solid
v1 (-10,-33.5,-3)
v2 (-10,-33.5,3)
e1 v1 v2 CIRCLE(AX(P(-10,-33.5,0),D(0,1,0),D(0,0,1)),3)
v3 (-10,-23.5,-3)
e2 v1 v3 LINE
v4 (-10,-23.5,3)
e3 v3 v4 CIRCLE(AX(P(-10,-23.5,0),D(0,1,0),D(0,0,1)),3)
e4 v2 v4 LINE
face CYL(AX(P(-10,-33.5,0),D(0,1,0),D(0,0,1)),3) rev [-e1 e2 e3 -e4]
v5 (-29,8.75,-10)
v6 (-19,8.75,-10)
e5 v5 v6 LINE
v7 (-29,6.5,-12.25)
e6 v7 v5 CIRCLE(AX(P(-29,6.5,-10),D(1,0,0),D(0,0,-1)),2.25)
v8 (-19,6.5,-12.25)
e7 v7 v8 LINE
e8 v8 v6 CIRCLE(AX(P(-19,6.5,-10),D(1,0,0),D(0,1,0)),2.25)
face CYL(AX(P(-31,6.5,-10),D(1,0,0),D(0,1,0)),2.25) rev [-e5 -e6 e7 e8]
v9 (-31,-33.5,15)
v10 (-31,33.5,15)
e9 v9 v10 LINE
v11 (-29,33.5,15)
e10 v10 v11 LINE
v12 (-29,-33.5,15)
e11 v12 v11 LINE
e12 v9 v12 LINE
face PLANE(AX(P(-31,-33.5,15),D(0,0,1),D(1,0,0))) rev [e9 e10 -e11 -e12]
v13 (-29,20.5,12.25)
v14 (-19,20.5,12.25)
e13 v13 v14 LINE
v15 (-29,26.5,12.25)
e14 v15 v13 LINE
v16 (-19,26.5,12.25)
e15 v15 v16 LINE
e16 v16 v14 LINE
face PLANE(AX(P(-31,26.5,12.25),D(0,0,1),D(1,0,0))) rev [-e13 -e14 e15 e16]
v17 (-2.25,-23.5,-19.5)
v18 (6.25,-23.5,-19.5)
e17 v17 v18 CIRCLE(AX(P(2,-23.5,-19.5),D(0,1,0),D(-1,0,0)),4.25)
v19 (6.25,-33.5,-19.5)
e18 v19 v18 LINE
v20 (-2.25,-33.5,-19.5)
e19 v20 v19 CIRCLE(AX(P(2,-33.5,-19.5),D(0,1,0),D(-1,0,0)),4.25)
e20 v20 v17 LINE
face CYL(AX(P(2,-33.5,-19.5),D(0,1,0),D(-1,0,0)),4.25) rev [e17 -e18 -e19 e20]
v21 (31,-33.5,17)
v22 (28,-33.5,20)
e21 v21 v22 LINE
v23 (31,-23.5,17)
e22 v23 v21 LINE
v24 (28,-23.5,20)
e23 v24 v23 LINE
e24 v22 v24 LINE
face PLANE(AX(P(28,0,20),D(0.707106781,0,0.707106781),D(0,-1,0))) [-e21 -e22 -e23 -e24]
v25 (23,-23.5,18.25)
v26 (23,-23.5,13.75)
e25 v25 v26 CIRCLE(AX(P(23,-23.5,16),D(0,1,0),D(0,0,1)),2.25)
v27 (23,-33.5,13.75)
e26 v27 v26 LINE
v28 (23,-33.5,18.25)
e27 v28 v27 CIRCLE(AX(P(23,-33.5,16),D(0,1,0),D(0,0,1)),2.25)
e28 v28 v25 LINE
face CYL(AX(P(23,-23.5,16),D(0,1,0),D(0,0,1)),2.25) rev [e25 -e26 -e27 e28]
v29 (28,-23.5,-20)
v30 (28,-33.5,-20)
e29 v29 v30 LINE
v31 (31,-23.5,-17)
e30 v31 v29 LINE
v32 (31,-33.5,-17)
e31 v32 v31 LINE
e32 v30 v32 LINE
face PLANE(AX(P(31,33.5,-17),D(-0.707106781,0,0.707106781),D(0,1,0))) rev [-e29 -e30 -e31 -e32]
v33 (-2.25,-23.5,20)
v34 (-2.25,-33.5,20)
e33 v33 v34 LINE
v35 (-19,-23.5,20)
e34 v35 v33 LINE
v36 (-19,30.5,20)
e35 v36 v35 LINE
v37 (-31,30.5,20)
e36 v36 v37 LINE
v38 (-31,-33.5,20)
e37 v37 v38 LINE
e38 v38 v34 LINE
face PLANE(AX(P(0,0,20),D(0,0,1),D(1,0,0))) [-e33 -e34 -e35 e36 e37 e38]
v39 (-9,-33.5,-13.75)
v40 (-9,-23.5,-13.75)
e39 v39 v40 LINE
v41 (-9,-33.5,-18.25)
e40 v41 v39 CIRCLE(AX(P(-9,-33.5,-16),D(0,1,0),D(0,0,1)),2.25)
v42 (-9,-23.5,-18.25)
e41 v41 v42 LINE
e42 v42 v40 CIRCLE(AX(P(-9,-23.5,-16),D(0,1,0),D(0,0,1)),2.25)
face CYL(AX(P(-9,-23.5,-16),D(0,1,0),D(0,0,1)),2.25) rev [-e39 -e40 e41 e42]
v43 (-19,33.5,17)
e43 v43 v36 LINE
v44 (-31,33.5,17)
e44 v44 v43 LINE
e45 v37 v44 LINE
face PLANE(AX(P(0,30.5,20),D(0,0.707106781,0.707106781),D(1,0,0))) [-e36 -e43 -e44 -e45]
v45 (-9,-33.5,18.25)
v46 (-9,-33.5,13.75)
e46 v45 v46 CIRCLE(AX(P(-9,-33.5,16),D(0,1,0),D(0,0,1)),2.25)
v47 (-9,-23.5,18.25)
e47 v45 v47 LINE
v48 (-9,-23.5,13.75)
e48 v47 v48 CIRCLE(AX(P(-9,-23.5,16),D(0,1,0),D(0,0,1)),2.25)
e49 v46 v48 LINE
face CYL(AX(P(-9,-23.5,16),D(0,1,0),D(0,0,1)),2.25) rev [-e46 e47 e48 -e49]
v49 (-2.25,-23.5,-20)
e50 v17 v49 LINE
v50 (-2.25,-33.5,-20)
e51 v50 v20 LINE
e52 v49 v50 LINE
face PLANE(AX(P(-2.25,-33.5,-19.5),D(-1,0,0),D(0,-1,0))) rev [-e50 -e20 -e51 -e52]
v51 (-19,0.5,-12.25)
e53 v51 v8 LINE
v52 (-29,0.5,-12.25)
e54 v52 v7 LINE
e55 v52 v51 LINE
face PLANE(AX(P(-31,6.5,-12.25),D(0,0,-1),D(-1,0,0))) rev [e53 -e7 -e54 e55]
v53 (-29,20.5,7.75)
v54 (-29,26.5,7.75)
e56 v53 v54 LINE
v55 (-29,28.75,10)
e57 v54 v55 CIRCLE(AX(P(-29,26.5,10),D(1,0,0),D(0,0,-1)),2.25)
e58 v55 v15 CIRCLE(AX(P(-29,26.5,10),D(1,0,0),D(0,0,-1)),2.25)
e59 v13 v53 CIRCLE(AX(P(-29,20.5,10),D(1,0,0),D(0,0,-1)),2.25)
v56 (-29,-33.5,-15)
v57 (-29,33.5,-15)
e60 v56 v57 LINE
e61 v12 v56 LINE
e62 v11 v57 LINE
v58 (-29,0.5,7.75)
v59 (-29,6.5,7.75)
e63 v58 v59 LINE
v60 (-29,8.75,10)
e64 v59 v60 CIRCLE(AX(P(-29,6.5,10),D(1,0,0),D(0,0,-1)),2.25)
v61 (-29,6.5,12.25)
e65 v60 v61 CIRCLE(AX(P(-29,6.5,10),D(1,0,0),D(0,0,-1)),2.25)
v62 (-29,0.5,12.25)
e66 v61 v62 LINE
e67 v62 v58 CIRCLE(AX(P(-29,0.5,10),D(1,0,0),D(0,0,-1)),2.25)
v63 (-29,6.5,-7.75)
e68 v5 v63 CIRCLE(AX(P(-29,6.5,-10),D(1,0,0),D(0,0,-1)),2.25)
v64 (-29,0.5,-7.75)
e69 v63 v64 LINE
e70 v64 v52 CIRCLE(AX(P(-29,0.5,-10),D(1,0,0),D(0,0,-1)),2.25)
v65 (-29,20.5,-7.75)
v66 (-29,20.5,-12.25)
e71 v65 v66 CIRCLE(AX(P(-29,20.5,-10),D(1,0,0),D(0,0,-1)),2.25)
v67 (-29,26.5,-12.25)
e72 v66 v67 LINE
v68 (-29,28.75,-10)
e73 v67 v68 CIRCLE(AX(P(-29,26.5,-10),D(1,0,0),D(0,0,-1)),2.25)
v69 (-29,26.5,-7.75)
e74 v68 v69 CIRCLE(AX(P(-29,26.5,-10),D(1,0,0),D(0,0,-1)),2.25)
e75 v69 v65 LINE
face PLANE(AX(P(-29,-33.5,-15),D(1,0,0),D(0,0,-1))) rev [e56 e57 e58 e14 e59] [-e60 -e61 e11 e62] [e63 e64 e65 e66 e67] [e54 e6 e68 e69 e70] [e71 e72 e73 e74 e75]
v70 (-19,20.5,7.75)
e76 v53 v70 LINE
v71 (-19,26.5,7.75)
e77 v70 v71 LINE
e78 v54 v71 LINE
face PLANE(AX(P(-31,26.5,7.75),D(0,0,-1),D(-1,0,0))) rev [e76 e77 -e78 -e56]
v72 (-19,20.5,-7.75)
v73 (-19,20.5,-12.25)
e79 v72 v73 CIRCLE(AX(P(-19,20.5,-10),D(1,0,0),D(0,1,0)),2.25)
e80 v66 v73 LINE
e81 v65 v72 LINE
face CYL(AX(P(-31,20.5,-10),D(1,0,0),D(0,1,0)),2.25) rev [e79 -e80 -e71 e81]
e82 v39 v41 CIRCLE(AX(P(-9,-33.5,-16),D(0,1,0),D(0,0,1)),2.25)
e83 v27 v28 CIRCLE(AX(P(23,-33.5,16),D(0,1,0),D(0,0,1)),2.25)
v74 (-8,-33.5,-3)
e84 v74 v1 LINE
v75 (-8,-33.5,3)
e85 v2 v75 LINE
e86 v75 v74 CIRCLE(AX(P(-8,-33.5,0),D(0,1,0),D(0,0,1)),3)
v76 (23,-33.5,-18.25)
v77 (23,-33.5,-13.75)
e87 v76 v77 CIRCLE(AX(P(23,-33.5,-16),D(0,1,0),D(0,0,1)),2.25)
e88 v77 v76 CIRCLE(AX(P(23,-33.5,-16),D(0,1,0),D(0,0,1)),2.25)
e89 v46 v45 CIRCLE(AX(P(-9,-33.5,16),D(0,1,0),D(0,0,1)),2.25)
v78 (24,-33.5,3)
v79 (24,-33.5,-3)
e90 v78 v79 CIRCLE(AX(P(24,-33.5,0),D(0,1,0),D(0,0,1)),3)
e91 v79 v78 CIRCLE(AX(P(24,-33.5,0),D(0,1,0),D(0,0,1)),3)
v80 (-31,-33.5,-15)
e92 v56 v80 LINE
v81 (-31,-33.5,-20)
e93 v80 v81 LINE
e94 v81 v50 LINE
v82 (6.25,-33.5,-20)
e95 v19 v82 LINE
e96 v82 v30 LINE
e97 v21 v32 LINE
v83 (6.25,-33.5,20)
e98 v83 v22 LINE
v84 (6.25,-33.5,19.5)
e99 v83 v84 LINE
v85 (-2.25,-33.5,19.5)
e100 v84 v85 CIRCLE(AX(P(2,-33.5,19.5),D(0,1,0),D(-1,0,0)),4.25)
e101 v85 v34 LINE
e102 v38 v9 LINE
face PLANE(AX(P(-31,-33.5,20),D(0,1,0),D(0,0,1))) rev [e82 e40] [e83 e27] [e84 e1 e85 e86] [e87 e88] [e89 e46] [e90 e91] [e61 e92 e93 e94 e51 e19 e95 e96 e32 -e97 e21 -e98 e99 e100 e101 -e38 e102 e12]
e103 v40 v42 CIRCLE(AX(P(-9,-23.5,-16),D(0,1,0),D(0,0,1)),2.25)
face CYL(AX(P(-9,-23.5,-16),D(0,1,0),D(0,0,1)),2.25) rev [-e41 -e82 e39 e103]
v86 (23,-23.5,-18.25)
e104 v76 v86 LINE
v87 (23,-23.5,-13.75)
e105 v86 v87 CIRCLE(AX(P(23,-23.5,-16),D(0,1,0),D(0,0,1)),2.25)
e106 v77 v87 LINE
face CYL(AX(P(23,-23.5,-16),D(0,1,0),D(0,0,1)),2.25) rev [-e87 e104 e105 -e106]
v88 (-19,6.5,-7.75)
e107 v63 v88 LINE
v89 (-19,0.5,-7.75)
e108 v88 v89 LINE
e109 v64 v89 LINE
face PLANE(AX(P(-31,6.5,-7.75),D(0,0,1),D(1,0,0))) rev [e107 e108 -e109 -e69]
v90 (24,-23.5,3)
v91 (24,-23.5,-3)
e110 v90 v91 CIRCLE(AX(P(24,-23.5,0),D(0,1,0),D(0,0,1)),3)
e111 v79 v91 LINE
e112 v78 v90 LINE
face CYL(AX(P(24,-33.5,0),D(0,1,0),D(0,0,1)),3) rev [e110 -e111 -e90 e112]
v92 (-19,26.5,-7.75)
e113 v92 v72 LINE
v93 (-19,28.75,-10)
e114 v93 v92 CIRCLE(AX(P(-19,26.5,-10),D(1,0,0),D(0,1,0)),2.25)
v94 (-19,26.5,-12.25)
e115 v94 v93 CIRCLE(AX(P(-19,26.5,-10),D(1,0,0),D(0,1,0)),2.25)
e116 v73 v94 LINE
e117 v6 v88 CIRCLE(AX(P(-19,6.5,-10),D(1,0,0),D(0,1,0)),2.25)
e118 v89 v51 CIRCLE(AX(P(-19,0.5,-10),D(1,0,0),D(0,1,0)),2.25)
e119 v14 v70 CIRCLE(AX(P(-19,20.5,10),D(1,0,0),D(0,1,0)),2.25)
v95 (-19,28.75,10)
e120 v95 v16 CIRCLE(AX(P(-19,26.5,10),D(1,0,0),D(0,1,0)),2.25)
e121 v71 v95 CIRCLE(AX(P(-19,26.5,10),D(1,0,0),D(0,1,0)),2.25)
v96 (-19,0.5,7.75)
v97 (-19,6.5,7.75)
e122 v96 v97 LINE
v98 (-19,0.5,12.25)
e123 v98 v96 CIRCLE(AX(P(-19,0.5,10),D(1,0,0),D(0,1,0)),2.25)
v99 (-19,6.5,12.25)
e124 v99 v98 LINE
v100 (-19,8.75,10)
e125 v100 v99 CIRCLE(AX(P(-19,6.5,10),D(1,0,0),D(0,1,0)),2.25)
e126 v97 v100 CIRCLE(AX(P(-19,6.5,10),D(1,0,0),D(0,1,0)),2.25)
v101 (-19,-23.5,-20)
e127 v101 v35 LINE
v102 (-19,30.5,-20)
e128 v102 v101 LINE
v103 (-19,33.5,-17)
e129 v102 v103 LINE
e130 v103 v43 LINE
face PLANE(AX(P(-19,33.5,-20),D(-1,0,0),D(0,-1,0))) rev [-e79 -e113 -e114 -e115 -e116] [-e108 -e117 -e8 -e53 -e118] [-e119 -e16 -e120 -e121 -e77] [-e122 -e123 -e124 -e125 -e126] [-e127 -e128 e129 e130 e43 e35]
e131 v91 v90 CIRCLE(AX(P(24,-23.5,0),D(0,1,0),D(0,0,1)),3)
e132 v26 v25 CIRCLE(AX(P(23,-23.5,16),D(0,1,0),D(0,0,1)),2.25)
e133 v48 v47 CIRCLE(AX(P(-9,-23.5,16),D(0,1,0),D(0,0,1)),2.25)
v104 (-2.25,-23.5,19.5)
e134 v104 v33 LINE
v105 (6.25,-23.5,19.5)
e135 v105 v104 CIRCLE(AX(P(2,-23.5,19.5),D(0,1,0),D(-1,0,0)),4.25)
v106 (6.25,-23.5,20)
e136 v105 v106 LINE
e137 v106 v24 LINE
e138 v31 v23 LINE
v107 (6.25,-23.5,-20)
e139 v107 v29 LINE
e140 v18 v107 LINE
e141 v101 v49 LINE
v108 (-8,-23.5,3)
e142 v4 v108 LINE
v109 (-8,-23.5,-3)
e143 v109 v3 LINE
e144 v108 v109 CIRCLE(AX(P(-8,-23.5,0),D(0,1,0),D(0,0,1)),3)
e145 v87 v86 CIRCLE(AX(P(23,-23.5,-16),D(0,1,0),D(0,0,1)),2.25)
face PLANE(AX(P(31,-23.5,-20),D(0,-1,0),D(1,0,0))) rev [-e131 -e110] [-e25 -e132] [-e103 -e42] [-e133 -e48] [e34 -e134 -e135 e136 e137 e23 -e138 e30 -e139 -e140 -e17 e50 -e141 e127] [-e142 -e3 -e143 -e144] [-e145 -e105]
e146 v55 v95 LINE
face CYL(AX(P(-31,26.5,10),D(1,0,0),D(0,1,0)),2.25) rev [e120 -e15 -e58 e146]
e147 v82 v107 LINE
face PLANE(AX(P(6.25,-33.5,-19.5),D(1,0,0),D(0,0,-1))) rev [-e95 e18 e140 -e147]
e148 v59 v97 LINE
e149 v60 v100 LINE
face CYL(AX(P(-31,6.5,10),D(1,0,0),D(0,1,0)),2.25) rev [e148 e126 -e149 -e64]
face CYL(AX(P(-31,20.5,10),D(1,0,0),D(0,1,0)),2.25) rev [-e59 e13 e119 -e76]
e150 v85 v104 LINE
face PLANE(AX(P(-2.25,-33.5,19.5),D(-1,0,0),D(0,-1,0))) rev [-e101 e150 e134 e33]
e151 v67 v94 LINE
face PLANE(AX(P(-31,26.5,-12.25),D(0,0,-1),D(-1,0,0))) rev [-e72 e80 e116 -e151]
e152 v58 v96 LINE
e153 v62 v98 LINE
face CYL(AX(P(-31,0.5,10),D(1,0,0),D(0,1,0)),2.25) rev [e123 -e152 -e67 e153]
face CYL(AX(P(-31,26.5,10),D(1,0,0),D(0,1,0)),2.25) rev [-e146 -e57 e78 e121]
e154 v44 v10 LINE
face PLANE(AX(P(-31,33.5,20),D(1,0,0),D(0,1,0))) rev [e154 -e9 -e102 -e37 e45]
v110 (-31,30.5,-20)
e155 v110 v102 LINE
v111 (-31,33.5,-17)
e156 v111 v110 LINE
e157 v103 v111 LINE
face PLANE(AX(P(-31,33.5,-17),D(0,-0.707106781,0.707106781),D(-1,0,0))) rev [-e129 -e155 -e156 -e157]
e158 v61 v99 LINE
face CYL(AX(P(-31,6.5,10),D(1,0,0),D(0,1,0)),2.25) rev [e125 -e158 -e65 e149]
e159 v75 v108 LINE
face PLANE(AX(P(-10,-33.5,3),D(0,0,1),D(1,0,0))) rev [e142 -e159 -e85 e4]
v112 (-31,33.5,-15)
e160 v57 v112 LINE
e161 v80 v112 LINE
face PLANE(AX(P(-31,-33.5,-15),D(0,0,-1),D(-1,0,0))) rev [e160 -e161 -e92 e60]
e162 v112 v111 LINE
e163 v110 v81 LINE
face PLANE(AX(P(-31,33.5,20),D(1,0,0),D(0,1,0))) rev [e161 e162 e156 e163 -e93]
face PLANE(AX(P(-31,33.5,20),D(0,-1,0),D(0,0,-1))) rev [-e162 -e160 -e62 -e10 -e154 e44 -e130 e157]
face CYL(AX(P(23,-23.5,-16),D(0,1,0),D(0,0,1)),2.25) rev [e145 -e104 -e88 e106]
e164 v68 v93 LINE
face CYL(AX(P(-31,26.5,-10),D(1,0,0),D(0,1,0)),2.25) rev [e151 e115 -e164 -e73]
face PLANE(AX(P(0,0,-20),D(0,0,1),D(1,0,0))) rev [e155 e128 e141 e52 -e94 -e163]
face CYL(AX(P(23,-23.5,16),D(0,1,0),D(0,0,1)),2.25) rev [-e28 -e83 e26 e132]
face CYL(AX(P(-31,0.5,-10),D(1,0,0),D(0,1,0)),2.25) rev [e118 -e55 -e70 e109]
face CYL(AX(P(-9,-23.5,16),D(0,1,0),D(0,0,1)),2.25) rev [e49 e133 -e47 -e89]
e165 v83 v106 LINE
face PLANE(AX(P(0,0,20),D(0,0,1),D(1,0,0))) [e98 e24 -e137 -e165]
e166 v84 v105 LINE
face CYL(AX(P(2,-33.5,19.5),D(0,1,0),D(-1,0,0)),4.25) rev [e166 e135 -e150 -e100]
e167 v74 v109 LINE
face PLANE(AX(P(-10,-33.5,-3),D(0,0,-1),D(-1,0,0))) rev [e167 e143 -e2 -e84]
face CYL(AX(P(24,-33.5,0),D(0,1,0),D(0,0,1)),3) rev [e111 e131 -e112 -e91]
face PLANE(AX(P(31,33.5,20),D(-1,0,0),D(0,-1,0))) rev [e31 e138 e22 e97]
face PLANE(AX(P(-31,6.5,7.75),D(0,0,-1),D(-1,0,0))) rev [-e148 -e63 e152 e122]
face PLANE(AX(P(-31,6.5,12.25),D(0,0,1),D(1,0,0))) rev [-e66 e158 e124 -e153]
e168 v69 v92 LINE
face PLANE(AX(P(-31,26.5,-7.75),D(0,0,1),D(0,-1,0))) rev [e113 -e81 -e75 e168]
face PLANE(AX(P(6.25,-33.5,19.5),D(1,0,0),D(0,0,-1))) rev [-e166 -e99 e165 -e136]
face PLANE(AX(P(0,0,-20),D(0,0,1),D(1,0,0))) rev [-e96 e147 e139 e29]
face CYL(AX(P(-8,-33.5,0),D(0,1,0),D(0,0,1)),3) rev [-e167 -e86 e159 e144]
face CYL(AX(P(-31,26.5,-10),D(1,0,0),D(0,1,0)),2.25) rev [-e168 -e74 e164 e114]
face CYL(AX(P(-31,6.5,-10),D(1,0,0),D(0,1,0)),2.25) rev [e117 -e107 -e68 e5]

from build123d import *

# Parameters (mm, degrees)
SKETCH1_W                  = 62
SKETCH1_H                  = 67
BOSS_EXTRUDE1_DEPTH        = 20
SKETCH2_W                  = 50
SKETCH2_H                  = 57
CUT_EXTRUDE1_DEPTH         = 61.689784972
SKETCH3_W                  = 2
SKETCH3_H                  = 30
CUT_EXTRUDE2_DEPTH         = 77.485292704
CUT_EXTRUDE3_DEPTH         = 64.421210963
F_4_5_4_5_DIAMETER_HOLE1_D = 4.5
SKETCH7_R                  = 3
CUT_EXTRUDE4_DEPTH         = 68.896980787
CHAMFER1_SIZE              = 3
CUT_EXTRUDE5_DEPTH         = 68.896980787


with BuildPart() as part:
    # Sketch1 → Boss-Extrude1 (new, symmetric)
    with BuildSketch(Plane.XY):
        Rectangle(SKETCH1_W, SKETCH1_H)
    extrude(amount=BOSS_EXTRUDE1_DEPTH, both=True)

    # Sketch2 → Cut-Extrude1 (cut, through all)
    with BuildSketch(Plane.XY.offset(20)):
        with Locations((6, 5)):
            Rectangle(SKETCH2_W, SKETCH2_H)
    extrude(amount=-CUT_EXTRUDE1_DEPTH, mode=Mode.SUBTRACT)

    # Sketch3 → Cut-Extrude2 (cut, through all)
    with BuildSketch(Plane(origin=(0, 33.5, 0), x_dir=(1, 0, 0), z_dir=(0, 1, 0))):
        with Locations((-30, 0)):
            Rectangle(SKETCH3_W, SKETCH3_H)
    extrude(amount=-CUT_EXTRUDE2_DEPTH, mode=Mode.SUBTRACT)

    # Sketch4 → Cut-Extrude3 (cut, through all)
    with BuildSketch(Plane(origin=(-19, 0, 0), x_dir=(0, 0, -1), z_dir=(1, 0, 0))):
        with BuildLine():
            Line((-7.75, 26.5), (-7.75, 20.5))
            ThreePointArc((-7.75, 20.5), (-10, 18.25), (-12.25, 20.5))
            Line((-12.25, 20.5), (-12.25, 26.5))
            ThreePointArc((-12.25, 26.5), (-10, 28.75), (-7.75, 26.5))
        make_face()
        with BuildLine():
            Line((-7.75, 6.5), (-7.75, 0.5))
            ThreePointArc((-7.75, 0.5), (-10, -1.75), (-12.25, 0.5))
            Line((-12.25, 0.5), (-12.25, 6.5))
            ThreePointArc((-12.25, 6.5), (-10, 8.75), (-7.75, 6.5))
        make_face()
        with BuildLine():
            Line((12.25, 26.5), (12.25, 20.5))
            ThreePointArc((12.25, 20.5), (10, 18.25), (7.75, 20.5))
            Line((7.75, 20.5), (7.75, 26.5))
            ThreePointArc((7.75, 26.5), (10, 28.75), (12.25, 26.5))
        make_face()
        with BuildLine():
            Line((12.25, 6.5), (12.25, 0.5))
            ThreePointArc((12.25, 0.5), (10, -1.75), (7.75, 0.5))
            Line((7.75, 0.5), (7.75, 6.5))
            ThreePointArc((7.75, 6.5), (10, 8.75), (12.25, 6.5))
        make_face()
    extrude(amount=-CUT_EXTRUDE3_DEPTH, mode=Mode.SUBTRACT)

    # Ø4.5 (4.5) Diameter Hole1 (through all)
    with Locations(Plane(origin=(0, -23.5, 0), x_dir=(1, 0, 0), z_dir=(0, 1, 0))):
        with Locations((-9, 16), (-9, -16), (23, -16), (23, 16)):
            Hole(F_4_5_4_5_DIAMETER_HOLE1_D / 2)

    # Sketch7 → Cut-Extrude4 (cut, through all)
    with BuildSketch(Plane(origin=(0, -23.5, 0), x_dir=(1, 0, 0), z_dir=(0, 1, 0))):
        with Locations(Location((24, 0, 0), (0, 0, 270))):
            Circle(SKETCH7_R)
        with BuildLine():
            Line((-10, 3), (-8, 3))
            ThreePointArc((-8, 3), (-5, 0), (-8, -3))
            Line((-8, -3), (-10, -3))
            ThreePointArc((-10, -3), (-13, 0), (-10, 3))
        make_face()
    extrude(amount=-CUT_EXTRUDE4_DEPTH, mode=Mode.SUBTRACT)

    # Chamfer1
    chamfer1_edges = [part.edges().sort_by_distance(p)[0] for p in [
        (-25, 33.5, -20),
        (-25, 33.5, 20),
        (31, -28.5, 20),
        (31, -28.5, -20),
    ]]
    chamfer(chamfer1_edges, length=CHAMFER1_SIZE)

    # Sketch8 → Cut-Extrude5 (cut, through all)
    with BuildSketch(Plane(origin=(0, -23.5, 0), x_dir=(1, 0, 0), z_dir=(0, 1, 0))):
        with BuildLine():
            Line((6.25, -19.5), (6.25, -27.0274699))
            ThreePointArc((6.25, -27.0274699), (2, -31.2774699), (-2.25, -27.0274699))
            Line((-2.25, -27.0274699), (-2.25, -19.5))
            ThreePointArc((-2.25, -19.5), (2, -15.25), (6.25, -19.5))
        make_face()
        with BuildLine():
            Line((-2.25, 19.5), (-2.25, 27.0274699))
            ThreePointArc((-2.25, 27.0274699), (2, 31.2774699), (6.25, 27.0274699))
            Line((6.25, 27.0274699), (6.25, 19.5))
            ThreePointArc((6.25, 19.5), (2, 15.25), (-2.25, 19.5))
        make_face()
    extrude(amount=-CUT_EXTRUDE5_DEPTH, mode=Mode.SUBTRACT)


solid = part.part
